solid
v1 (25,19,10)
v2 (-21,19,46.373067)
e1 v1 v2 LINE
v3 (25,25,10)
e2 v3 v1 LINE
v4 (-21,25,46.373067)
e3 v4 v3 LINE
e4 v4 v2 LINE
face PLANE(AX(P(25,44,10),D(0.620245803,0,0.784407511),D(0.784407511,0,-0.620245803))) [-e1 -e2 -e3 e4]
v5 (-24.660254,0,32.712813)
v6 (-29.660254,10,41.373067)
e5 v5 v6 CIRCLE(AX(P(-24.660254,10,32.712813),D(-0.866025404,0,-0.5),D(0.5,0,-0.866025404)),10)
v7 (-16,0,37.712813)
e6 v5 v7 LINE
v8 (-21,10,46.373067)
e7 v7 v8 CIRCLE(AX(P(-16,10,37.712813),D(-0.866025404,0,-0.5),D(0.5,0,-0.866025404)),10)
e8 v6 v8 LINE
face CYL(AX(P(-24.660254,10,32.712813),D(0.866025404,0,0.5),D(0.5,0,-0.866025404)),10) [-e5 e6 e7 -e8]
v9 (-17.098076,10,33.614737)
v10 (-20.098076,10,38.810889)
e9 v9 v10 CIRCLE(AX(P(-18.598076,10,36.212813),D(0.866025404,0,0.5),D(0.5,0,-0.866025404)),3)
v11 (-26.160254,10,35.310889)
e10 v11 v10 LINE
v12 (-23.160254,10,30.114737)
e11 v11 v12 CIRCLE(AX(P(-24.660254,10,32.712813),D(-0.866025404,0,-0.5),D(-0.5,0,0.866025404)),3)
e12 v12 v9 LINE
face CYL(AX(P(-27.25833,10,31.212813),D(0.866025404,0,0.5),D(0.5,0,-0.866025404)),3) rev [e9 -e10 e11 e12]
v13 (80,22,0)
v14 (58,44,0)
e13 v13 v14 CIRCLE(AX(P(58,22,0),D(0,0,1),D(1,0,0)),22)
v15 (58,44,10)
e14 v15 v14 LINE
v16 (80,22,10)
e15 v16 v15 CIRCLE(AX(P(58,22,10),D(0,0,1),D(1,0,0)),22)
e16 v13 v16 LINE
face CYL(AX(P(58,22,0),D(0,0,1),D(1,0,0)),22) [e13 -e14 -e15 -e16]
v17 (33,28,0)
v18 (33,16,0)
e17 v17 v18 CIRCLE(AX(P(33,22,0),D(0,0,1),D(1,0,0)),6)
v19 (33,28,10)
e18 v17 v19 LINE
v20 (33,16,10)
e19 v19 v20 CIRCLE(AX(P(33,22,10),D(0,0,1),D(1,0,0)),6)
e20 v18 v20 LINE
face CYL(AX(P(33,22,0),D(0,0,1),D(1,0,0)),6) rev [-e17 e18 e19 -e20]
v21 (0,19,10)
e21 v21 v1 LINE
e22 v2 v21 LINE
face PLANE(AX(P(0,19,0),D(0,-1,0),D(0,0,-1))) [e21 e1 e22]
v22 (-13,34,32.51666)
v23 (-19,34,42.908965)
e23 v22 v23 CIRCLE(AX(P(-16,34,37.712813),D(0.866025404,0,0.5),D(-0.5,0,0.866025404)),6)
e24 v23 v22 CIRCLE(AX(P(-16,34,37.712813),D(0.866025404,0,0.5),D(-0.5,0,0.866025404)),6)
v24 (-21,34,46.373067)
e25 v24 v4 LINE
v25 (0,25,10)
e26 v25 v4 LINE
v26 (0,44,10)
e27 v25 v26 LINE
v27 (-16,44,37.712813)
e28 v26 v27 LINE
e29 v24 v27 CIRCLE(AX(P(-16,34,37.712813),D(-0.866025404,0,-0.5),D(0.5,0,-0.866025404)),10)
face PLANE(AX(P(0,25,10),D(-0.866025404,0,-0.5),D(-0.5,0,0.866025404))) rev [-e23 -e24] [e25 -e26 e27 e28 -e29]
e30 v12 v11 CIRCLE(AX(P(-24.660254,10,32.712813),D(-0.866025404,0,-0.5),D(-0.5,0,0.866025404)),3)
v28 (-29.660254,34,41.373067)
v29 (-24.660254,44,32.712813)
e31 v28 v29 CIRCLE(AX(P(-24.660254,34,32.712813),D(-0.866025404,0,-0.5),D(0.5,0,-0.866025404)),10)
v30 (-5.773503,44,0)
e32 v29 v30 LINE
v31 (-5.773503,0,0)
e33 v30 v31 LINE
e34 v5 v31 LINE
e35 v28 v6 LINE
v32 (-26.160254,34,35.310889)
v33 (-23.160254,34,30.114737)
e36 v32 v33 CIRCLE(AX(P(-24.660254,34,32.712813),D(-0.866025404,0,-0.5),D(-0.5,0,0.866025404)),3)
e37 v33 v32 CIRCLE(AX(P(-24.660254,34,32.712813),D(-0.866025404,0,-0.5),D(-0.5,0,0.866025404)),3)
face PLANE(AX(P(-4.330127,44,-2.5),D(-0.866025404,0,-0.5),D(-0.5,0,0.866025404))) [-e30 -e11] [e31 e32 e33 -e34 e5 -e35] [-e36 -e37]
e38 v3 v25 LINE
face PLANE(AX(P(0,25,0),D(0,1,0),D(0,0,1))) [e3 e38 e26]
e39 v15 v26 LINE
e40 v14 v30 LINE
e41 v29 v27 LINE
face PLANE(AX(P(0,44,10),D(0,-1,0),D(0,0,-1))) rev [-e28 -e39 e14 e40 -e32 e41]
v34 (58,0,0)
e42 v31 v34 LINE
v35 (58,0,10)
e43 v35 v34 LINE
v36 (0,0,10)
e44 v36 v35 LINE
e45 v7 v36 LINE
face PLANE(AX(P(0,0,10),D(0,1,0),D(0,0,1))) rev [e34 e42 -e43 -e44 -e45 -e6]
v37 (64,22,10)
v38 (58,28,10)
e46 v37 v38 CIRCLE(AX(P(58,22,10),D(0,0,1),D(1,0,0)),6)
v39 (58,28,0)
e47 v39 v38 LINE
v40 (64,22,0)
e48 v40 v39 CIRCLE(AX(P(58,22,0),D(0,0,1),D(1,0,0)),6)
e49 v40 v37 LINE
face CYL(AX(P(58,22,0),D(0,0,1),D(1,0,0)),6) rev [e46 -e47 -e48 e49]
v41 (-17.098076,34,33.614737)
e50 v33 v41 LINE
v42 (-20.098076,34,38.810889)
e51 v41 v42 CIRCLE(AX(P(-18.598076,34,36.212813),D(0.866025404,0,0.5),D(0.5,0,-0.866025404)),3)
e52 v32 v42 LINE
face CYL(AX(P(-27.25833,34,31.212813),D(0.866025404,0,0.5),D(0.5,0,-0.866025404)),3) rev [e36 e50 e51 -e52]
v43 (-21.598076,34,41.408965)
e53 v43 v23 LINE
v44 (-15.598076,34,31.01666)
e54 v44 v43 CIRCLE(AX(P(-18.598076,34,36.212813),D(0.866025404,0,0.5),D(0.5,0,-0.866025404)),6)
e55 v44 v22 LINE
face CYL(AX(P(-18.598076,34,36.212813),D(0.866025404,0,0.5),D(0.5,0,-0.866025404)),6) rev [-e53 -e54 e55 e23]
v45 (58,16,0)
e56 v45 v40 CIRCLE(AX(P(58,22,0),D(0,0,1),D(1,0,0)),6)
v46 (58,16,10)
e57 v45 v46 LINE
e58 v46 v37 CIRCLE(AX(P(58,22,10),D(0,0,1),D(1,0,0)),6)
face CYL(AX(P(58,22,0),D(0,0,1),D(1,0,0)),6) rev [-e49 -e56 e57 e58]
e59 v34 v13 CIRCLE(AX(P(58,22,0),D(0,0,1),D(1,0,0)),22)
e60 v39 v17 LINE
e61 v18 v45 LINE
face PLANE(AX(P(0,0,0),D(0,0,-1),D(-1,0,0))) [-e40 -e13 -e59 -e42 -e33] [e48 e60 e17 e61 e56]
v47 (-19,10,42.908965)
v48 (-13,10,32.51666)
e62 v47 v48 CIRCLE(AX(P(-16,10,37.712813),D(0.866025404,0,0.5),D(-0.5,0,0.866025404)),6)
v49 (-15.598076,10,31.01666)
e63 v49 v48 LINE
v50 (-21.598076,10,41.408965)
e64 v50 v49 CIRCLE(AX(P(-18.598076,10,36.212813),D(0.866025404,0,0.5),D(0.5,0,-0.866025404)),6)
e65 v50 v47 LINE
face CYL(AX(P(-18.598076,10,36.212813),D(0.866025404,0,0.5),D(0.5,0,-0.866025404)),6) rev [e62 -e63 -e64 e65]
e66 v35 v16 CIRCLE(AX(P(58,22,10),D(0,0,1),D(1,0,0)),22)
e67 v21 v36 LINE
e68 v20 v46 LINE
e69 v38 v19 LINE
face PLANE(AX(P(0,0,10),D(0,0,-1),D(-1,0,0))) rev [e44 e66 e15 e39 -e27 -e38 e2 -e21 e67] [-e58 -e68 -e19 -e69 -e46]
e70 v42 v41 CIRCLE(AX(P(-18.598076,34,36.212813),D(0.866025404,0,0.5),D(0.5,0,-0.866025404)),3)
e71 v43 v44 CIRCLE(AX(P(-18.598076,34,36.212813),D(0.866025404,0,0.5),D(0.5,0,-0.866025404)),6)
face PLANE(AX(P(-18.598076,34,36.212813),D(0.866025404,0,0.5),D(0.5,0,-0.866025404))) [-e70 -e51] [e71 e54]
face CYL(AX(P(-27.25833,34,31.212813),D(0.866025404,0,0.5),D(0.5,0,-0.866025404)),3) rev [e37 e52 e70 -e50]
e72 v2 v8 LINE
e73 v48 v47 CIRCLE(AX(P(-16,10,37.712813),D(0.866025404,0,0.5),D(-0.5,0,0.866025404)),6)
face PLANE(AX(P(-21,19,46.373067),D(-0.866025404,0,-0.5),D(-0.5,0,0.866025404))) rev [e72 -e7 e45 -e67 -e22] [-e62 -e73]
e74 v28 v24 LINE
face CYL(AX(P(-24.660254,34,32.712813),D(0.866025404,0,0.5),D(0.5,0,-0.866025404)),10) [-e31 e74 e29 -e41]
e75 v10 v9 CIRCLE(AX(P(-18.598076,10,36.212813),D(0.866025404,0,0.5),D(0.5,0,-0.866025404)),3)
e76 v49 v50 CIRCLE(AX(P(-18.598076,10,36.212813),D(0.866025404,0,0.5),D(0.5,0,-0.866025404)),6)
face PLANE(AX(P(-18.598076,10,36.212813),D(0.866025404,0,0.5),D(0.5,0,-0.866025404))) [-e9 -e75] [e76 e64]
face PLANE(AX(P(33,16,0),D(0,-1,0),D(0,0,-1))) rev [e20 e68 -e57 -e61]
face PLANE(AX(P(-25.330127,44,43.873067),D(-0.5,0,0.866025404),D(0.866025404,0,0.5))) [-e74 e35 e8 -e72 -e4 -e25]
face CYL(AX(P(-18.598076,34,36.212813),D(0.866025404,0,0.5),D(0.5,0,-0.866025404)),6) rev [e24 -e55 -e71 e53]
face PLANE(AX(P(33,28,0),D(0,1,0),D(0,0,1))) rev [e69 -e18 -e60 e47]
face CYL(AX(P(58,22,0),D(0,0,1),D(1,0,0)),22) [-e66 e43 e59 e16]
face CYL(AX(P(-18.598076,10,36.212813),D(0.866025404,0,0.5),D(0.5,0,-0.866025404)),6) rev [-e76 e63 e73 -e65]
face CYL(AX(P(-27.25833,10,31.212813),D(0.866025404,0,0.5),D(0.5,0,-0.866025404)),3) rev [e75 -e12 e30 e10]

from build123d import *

# Parameters (mm, degrees)
BASE_PLATE_SKETCH_W        = 58
BASE_PLATE_SKETCH_H        = 44
BASE_PLATE_58X44X10_DEPTH  = 10
BASE_ROUNDED_END_SKETCH_R  = 22
BASE_ROUNDED_END_R22_DEPTH = 10
BASE_SLOT_DEPTH            = 10
ANGLED_ARM_120DEG_DEPTH    = 44
ARM_END_TRIM_DEPTH         = 10
COUNTERBORE_SKETCH_R       = 6
COUNTERBORES_2X_12X3_DEPTH = 3
ARM_HOLE_SKETCH_R          = 3
ARM_HOLES_2X_6_DEPTH       = 10
GUSSET_BLANK_DEPTH         = 44
GUSSET_SIDE_TRIM_1_DEPTH   = 19
GUSSET_SIDE_TRIM_2_DEPTH   = 19


with BuildPart() as part:
    # Base Plate Sketch → Base Plate 58x44x10 (new body)
    with BuildSketch(Plane.XY):
        with Locations((29, 22)):
            Rectangle(BASE_PLATE_SKETCH_W, BASE_PLATE_SKETCH_H)
    extrude(amount=BASE_PLATE_58X44X10_DEPTH)

    # Base Rounded End Sketch → Base Rounded End R22 (add)
    with BuildSketch(Plane.XY.offset(10)):
        with Locations((58, 22)):
            Circle(BASE_ROUNDED_END_SKETCH_R)
    extrude(amount=-BASE_ROUNDED_END_R22_DEPTH)

    # Base Slot Sketch → Base Slot (cut)
    with BuildSketch(Plane.XY.offset(10)):
        with BuildLine():
            Line((33, 28), (58, 28))
            ThreePointArc((58, 28), (64, 22), (58, 16))
            Line((58, 16), (33, 16))
            ThreePointArc((33, 16), (27, 22), (33, 28))
        make_face()
    extrude(amount=-BASE_SLOT_DEPTH, mode=Mode.SUBTRACT)

    # Angled Arm Sketch → Angled Arm 120deg (add)
    with BuildSketch(Plane.XZ):
        Polygon((-29.660254038, 41.373066959), (-5.773502692, 0), (0, 0), (0, 10), (-21, 46.373066959), align=None)
    extrude(amount=-ANGLED_ARM_120DEG_DEPTH)

    # Arm End Trim Sketch → Arm End Trim (cut)
    with BuildSketch(Plane(origin=(4.330127019, 0, 2.5), x_dir=(0.5000000000000042, 0, -0.8660254037844363), z_dir=(0.8660254037844363, 0, 0.5000000000000042))):
        with BuildLine():
            Line((-50.660254038, 0), (-40.660254038, 0))
            ThreePointArc((-40.660254038, 0), (-47.73132185, 2.928932188), (-50.660254038, 10))
            Line((-50.660254038, 10), (-50.660254038, 0))
        make_face()
        with BuildLine():
            Line((-50.660254038, 44), (-40.660254038, 44))
            ThreePointArc((-40.660254038, 44), (-47.73132185, 41.071067812), (-50.660254038, 34))
            Line((-50.660254038, 34), (-50.660254038, 44))
        make_face()
    extrude(amount=-ARM_END_TRIM_DEPTH, mode=Mode.SUBTRACT)

    # Counterbore Sketch → Counterbores 2xØ12x3 (cut)
    with BuildSketch(Plane(origin=(4.330127019, 0, 2.5), x_dir=(0.5000000000000042, 0, -0.8660254037844363), z_dir=(0.8660254037844363, 0, 0.5000000000000042))):
        with Locations((-40.660254038, 34)):
            Circle(COUNTERBORE_SKETCH_R)
        with Locations((-40.660254038, 10)):
            Circle(COUNTERBORE_SKETCH_R)
    extrude(amount=-COUNTERBORES_2X_12X3_DEPTH, mode=Mode.SUBTRACT)

    # Arm Hole Sketch → Arm Holes 2xØ6 (cut)
    with BuildSketch(Plane(origin=(1.732050808, 0, 1), x_dir=(0.5000000000000042, 0, -0.8660254037844363), z_dir=(0.8660254037844363, 0, 0.5000000000000042))):
        with Locations((-40.660254038, 34)):
            Circle(ARM_HOLE_SKETCH_R)
        with Locations((-40.660254038, 10)):
            Circle(ARM_HOLE_SKETCH_R)
    extrude(amount=-ARM_HOLES_2X_6_DEPTH, mode=Mode.SUBTRACT)

    # Gusset Profile Sketch → Gusset Blank (add)
    with BuildSketch(Plane.XZ):
        Polygon((0, 10), (25, 10), (-21, 46.373066959), align=None)
    extrude(amount=-GUSSET_BLANK_DEPTH)

    # Gusset Side Trim 1 Sketch → Gusset Side Trim 1 (cut)
    with BuildSketch(Plane.XZ):
        Polygon((4.891585761, 10), (25, 10), (-21, 46.373066959), (0, 10), align=None)
    extrude(amount=-GUSSET_SIDE_TRIM_1_DEPTH, mode=Mode.SUBTRACT)

    # Gusset Side Trim 2 Sketch → Gusset Side Trim 2 (cut)
    with BuildSketch(Plane(origin=(0, 44, 0), x_dir=(1, 0, 0), z_dir=(0, 1, 0))):
        Polygon((25, -10), (0, -10), (-21, -46.373066959), align=None)
    extrude(amount=-GUSSET_SIDE_TRIM_2_DEPTH, mode=Mode.SUBTRACT)


solid = part.part
